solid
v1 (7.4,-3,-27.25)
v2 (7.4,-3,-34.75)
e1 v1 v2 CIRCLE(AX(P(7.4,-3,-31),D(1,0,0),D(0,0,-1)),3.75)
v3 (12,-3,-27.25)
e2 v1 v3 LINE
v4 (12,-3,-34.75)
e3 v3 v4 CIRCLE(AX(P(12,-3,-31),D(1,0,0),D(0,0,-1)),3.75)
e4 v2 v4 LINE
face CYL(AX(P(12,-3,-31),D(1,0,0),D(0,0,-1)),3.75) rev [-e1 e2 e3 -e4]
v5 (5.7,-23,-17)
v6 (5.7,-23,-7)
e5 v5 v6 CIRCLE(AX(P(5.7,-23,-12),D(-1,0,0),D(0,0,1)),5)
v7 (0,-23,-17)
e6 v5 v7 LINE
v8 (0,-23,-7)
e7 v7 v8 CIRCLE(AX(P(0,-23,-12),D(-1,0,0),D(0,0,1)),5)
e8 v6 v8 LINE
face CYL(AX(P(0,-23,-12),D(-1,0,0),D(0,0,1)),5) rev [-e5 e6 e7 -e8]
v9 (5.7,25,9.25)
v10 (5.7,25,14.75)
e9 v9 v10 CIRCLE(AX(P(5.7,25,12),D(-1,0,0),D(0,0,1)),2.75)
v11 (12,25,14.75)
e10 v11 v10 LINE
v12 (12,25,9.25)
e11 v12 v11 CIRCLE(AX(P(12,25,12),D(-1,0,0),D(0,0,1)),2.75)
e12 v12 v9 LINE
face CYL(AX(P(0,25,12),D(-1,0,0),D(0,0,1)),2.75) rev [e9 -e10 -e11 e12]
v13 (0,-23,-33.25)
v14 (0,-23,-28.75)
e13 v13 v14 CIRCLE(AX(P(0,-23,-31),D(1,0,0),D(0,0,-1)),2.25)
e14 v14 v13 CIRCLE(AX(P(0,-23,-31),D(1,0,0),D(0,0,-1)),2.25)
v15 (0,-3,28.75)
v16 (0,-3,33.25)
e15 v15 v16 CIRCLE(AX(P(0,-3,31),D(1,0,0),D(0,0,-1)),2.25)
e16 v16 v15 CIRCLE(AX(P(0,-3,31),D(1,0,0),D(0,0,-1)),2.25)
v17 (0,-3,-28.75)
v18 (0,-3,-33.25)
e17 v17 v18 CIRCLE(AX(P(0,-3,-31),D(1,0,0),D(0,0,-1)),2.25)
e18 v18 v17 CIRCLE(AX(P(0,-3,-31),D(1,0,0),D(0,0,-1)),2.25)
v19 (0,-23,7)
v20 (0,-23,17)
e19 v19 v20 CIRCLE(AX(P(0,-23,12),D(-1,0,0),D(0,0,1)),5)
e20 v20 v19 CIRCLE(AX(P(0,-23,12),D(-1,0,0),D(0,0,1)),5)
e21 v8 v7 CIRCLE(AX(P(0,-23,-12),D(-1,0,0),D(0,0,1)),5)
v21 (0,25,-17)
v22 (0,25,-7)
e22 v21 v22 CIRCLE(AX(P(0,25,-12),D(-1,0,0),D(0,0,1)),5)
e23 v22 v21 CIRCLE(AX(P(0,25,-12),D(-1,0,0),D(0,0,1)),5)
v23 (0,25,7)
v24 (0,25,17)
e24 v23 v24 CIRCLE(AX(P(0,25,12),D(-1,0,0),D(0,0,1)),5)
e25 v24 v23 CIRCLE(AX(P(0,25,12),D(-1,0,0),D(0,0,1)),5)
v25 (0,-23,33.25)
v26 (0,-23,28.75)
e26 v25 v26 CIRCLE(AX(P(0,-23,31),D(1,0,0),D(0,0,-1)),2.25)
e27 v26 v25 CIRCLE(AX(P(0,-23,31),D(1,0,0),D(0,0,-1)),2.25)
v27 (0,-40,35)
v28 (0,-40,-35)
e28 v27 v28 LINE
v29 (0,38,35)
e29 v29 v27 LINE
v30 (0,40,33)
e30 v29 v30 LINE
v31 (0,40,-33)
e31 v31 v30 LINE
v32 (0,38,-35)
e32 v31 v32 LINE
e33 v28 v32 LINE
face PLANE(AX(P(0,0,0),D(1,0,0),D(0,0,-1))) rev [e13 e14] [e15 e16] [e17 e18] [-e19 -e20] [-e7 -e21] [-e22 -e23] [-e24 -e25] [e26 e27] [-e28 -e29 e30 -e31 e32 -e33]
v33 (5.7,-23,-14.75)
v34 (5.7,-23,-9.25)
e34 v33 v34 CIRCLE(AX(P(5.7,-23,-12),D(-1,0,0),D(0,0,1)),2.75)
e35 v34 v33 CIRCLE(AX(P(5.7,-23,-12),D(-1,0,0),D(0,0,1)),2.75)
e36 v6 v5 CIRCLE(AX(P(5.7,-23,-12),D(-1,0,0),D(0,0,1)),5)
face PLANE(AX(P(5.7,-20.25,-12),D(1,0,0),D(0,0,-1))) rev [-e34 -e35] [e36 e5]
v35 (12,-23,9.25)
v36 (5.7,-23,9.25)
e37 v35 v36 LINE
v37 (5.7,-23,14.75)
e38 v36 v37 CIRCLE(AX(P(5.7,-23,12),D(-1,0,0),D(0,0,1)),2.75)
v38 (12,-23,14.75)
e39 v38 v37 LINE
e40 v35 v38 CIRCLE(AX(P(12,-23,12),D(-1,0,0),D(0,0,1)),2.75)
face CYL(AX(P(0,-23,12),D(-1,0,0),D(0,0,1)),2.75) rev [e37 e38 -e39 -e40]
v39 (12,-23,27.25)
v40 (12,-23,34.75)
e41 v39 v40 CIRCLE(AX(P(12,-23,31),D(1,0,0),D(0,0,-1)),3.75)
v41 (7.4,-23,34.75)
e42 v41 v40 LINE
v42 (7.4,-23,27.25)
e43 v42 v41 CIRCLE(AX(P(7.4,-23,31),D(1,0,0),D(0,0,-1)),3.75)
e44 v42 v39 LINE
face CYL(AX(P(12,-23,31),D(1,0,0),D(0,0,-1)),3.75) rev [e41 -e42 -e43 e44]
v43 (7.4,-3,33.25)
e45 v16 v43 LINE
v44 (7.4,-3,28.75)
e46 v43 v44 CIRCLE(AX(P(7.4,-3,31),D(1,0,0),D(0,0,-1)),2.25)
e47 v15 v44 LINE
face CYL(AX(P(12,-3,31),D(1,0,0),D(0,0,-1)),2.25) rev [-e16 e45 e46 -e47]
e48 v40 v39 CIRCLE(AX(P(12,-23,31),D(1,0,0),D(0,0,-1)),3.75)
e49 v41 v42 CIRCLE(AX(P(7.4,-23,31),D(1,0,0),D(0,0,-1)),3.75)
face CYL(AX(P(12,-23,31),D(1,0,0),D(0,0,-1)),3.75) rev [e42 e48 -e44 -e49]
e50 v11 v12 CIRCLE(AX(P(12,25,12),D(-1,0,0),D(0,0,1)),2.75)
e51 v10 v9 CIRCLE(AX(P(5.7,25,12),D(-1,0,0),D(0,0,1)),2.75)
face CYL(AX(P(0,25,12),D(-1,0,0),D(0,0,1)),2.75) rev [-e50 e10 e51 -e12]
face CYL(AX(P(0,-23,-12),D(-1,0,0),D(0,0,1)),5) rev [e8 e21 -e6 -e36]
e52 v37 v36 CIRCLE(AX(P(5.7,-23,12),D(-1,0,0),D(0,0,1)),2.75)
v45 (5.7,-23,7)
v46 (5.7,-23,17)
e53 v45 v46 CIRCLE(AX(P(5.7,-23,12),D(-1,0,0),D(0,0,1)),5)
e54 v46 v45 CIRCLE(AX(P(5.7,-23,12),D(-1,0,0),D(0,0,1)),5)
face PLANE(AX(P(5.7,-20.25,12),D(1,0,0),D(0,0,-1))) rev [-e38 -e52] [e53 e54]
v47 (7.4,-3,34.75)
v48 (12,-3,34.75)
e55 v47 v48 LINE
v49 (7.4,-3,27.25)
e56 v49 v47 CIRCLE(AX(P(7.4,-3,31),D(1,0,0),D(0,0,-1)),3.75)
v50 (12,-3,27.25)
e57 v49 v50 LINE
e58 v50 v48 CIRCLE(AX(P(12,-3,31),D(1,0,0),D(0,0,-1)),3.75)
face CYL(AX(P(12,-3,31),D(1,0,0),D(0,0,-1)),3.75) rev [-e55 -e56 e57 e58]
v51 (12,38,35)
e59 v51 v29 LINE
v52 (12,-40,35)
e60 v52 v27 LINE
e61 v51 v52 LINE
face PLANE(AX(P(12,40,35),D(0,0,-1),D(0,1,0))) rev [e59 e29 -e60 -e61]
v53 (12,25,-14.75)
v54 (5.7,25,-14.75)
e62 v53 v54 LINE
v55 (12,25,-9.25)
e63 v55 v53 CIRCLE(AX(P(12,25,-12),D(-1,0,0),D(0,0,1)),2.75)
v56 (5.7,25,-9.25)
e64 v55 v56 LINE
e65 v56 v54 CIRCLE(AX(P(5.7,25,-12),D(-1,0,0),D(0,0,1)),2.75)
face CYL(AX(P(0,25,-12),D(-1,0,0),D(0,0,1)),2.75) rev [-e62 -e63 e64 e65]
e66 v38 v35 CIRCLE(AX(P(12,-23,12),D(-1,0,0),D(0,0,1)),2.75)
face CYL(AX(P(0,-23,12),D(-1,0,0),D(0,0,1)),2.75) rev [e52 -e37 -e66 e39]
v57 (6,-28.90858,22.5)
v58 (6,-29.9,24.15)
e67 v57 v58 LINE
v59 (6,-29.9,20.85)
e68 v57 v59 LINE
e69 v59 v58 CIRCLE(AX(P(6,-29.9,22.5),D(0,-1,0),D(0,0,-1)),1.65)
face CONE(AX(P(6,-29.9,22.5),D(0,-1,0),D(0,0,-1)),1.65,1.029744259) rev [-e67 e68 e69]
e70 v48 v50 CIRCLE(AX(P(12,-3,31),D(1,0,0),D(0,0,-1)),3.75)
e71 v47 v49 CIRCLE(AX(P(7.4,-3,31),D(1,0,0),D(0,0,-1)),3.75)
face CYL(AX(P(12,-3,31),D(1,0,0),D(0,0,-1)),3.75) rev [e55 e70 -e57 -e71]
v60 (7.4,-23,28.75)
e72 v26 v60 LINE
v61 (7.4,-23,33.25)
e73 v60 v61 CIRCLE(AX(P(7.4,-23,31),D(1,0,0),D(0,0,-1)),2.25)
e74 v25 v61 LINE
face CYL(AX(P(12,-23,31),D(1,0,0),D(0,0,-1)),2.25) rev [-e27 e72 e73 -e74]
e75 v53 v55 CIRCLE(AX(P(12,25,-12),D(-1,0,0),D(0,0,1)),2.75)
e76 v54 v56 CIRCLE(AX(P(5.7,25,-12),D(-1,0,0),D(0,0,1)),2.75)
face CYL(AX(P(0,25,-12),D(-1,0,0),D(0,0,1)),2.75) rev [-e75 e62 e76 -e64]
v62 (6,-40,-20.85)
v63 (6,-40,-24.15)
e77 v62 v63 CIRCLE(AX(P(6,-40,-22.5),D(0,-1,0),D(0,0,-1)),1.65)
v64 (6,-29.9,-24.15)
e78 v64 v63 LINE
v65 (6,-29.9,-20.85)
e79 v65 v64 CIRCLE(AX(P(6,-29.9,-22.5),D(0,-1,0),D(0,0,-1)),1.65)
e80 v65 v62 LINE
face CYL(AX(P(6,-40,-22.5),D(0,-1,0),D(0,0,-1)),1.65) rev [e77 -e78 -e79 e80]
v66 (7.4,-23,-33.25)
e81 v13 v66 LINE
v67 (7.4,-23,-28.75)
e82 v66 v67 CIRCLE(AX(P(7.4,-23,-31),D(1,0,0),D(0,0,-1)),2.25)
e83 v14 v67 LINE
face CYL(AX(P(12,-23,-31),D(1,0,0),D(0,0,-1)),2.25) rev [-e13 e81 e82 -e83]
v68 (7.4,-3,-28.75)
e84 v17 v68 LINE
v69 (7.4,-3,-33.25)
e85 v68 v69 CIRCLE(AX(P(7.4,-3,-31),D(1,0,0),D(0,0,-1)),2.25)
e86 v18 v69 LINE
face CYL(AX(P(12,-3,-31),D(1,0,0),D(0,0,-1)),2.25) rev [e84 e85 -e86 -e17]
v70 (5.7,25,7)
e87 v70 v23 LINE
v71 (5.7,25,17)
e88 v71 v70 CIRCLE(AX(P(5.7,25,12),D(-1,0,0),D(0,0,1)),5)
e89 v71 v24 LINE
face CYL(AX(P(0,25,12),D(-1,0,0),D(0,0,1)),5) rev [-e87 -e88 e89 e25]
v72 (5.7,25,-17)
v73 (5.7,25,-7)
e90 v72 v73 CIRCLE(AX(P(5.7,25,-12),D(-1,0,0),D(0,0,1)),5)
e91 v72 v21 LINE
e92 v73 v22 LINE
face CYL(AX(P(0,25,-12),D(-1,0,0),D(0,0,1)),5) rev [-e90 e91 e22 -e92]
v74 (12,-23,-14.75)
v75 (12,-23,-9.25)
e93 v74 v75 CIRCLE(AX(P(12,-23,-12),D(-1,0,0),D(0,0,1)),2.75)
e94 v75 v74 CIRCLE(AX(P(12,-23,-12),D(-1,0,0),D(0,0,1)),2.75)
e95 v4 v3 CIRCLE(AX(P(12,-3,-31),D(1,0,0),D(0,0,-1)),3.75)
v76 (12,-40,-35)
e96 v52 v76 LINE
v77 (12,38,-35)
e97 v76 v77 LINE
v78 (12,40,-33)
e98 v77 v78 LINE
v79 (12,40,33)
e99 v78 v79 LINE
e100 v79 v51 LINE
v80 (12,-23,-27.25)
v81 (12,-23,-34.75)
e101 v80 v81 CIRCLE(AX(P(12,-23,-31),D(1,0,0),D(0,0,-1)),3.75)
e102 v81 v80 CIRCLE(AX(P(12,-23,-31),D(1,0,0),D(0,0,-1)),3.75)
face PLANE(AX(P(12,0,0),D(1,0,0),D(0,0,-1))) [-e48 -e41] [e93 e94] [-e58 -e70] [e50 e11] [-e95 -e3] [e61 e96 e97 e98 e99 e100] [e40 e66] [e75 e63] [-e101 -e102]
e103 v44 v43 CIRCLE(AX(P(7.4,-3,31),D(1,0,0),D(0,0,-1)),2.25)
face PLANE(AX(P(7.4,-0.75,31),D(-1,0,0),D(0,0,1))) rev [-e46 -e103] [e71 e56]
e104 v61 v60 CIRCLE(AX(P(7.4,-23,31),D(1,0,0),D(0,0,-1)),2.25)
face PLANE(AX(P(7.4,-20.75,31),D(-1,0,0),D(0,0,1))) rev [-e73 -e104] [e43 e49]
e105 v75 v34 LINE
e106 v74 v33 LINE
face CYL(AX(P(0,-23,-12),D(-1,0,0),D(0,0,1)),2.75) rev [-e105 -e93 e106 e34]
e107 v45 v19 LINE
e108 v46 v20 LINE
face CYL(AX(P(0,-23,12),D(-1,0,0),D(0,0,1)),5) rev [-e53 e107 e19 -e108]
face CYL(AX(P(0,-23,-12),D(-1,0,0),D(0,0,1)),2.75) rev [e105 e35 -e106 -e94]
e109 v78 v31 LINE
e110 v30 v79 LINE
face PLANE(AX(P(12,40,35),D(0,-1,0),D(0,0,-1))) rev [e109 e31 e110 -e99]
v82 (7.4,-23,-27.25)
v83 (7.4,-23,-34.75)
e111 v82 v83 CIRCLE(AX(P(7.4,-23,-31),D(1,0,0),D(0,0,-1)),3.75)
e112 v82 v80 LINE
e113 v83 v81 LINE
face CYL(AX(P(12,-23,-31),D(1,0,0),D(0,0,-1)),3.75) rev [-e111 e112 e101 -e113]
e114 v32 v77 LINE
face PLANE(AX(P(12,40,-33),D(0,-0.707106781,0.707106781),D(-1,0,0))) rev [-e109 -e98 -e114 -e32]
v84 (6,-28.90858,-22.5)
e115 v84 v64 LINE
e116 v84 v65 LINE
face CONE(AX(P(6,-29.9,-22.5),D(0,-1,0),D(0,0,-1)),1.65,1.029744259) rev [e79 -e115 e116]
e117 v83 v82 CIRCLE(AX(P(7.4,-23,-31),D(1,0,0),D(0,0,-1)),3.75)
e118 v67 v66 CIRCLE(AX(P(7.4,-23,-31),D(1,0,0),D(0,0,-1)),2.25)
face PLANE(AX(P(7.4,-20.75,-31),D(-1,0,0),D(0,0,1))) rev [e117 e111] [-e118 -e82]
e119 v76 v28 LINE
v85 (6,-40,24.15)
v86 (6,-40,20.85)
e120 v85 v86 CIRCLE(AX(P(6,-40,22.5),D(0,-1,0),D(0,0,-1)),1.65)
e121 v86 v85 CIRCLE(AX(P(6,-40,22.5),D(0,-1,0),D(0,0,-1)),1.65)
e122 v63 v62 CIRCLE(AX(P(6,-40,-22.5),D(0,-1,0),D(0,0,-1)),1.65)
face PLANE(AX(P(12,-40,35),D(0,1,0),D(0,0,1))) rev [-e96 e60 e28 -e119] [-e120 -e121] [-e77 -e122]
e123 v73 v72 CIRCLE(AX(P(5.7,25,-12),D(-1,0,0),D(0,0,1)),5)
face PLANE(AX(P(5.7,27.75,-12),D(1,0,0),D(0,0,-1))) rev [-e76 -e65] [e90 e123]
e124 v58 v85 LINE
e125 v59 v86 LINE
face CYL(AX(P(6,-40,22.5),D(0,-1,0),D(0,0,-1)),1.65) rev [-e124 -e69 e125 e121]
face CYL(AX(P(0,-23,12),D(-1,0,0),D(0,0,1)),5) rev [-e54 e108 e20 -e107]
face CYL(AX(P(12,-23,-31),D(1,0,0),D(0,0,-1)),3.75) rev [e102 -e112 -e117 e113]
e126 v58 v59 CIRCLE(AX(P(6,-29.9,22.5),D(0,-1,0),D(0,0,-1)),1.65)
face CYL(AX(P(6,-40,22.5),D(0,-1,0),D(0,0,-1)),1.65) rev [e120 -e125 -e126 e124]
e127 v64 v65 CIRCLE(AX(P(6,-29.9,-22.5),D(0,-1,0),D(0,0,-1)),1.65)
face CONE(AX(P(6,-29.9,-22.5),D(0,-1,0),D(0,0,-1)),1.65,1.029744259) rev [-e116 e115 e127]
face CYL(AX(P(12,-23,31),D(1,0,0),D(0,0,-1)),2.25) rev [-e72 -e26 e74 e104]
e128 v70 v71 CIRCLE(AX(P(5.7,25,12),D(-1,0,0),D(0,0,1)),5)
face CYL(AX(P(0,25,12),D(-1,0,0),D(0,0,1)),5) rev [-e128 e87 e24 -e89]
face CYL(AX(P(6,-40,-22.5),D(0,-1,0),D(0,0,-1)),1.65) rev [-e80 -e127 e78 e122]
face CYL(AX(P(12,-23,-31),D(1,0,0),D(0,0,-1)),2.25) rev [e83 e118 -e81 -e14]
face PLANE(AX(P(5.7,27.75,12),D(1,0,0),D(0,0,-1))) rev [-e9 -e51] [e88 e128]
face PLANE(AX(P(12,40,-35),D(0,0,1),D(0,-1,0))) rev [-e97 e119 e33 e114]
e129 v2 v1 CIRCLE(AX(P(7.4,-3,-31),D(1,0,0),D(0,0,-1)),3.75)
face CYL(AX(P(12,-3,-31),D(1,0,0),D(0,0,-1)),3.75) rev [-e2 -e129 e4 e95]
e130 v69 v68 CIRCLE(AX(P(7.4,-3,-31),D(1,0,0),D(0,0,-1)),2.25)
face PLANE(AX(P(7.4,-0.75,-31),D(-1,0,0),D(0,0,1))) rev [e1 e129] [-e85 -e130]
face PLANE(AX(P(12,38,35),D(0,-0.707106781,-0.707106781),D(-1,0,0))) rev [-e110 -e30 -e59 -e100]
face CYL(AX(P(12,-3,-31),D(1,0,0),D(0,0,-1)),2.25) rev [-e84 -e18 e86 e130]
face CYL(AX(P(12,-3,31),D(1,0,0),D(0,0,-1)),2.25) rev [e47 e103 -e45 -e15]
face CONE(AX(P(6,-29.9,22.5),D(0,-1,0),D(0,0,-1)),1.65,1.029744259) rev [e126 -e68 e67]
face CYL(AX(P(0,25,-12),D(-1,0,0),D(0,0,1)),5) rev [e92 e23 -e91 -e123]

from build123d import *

# Parameters (mm, degrees)
SKETCH_1_W                   = 70
SKETCH_1_H                   = 80
EXTRUDE_1_DEPTH              = 12
HOLE_WIZARD_M5_1_D           = 5.5
HOLE_WIZARD_M5_1_CBORE_D     = 10
HOLE_WIZARD_M5_1_CBORE_DEPTH = 5.7
HOLE_WIZARD_M4_1_D           = 4.5
HOLE_WIZARD_M4_1_CBORE_D     = 7.5
HOLE_WIZARD_M4_1_CBORE_DEPTH = 4.6
HOLE_WIZARD_M4_1_2_D         = 3.3
HOLE_WIZARD_M4_1_2_DEPTH     = 10.1
HOLE_WIZARD_M4_1_2_TIP       = 0.991420021
CHAMFER_1_SIZE               = 2


with BuildPart() as part:
    # 草图1 → 凸台-拉伸1 (new body)
    with BuildSketch(Plane(origin=(0, 0, 0), x_dir=(0, 0, -1), z_dir=(1, 0, 0))):
        Rectangle(SKETCH_1_W, SKETCH_1_H)
    extrude(amount=EXTRUDE_1_DEPTH)

    # M5 六角圆柱头螺钉的柱形沉头孔1 (through all)
    with Locations(Plane.ZY):
        with Locations((-12, 25), (-12, -23), (12, -23), (12, 25)):
            CounterBoreHole(HOLE_WIZARD_M5_1_D / 2, HOLE_WIZARD_M5_1_CBORE_D / 2, HOLE_WIZARD_M5_1_CBORE_DEPTH)

    # Hole Wizard M4 _1 (through all)
    with Locations(Plane(origin=(12, 0, 0), x_dir=(0, 0, -1), z_dir=(1, 0, 0))):
        with Locations((-31, -23), (-31, -3), (31, -3), (31, -23)):
            CounterBoreHole(HOLE_WIZARD_M4_1_D / 2, HOLE_WIZARD_M4_1_CBORE_D / 2, HOLE_WIZARD_M4_1_CBORE_DEPTH)

    # Hole Wizard M4 _1 2
    with Locations(Plane(origin=(0, -40, 0), x_dir=(-1, 0, 0), z_dir=(0, -1, 0))):
        with Locations((-6, 22.5), (-6, -22.5)):
            Hole(HOLE_WIZARD_M4_1_2_D / 2, depth=HOLE_WIZARD_M4_1_2_DEPTH)
            with Locations((0, 0, -(HOLE_WIZARD_M4_1_2_DEPTH + HOLE_WIZARD_M4_1_2_TIP / 2))):  # 118° drill point
                Cone(0, HOLE_WIZARD_M4_1_2_D / 2, HOLE_WIZARD_M4_1_2_TIP, mode=Mode.SUBTRACT)

    # 倒角1
    chamfer_1_edges = [part.edges().sort_by_distance(p)[0] for p in [
        (6, 40, 35),
        (6, 40, -35),
    ]]
    chamfer(chamfer_1_edges, length=CHAMFER_1_SIZE)


solid = part.part
